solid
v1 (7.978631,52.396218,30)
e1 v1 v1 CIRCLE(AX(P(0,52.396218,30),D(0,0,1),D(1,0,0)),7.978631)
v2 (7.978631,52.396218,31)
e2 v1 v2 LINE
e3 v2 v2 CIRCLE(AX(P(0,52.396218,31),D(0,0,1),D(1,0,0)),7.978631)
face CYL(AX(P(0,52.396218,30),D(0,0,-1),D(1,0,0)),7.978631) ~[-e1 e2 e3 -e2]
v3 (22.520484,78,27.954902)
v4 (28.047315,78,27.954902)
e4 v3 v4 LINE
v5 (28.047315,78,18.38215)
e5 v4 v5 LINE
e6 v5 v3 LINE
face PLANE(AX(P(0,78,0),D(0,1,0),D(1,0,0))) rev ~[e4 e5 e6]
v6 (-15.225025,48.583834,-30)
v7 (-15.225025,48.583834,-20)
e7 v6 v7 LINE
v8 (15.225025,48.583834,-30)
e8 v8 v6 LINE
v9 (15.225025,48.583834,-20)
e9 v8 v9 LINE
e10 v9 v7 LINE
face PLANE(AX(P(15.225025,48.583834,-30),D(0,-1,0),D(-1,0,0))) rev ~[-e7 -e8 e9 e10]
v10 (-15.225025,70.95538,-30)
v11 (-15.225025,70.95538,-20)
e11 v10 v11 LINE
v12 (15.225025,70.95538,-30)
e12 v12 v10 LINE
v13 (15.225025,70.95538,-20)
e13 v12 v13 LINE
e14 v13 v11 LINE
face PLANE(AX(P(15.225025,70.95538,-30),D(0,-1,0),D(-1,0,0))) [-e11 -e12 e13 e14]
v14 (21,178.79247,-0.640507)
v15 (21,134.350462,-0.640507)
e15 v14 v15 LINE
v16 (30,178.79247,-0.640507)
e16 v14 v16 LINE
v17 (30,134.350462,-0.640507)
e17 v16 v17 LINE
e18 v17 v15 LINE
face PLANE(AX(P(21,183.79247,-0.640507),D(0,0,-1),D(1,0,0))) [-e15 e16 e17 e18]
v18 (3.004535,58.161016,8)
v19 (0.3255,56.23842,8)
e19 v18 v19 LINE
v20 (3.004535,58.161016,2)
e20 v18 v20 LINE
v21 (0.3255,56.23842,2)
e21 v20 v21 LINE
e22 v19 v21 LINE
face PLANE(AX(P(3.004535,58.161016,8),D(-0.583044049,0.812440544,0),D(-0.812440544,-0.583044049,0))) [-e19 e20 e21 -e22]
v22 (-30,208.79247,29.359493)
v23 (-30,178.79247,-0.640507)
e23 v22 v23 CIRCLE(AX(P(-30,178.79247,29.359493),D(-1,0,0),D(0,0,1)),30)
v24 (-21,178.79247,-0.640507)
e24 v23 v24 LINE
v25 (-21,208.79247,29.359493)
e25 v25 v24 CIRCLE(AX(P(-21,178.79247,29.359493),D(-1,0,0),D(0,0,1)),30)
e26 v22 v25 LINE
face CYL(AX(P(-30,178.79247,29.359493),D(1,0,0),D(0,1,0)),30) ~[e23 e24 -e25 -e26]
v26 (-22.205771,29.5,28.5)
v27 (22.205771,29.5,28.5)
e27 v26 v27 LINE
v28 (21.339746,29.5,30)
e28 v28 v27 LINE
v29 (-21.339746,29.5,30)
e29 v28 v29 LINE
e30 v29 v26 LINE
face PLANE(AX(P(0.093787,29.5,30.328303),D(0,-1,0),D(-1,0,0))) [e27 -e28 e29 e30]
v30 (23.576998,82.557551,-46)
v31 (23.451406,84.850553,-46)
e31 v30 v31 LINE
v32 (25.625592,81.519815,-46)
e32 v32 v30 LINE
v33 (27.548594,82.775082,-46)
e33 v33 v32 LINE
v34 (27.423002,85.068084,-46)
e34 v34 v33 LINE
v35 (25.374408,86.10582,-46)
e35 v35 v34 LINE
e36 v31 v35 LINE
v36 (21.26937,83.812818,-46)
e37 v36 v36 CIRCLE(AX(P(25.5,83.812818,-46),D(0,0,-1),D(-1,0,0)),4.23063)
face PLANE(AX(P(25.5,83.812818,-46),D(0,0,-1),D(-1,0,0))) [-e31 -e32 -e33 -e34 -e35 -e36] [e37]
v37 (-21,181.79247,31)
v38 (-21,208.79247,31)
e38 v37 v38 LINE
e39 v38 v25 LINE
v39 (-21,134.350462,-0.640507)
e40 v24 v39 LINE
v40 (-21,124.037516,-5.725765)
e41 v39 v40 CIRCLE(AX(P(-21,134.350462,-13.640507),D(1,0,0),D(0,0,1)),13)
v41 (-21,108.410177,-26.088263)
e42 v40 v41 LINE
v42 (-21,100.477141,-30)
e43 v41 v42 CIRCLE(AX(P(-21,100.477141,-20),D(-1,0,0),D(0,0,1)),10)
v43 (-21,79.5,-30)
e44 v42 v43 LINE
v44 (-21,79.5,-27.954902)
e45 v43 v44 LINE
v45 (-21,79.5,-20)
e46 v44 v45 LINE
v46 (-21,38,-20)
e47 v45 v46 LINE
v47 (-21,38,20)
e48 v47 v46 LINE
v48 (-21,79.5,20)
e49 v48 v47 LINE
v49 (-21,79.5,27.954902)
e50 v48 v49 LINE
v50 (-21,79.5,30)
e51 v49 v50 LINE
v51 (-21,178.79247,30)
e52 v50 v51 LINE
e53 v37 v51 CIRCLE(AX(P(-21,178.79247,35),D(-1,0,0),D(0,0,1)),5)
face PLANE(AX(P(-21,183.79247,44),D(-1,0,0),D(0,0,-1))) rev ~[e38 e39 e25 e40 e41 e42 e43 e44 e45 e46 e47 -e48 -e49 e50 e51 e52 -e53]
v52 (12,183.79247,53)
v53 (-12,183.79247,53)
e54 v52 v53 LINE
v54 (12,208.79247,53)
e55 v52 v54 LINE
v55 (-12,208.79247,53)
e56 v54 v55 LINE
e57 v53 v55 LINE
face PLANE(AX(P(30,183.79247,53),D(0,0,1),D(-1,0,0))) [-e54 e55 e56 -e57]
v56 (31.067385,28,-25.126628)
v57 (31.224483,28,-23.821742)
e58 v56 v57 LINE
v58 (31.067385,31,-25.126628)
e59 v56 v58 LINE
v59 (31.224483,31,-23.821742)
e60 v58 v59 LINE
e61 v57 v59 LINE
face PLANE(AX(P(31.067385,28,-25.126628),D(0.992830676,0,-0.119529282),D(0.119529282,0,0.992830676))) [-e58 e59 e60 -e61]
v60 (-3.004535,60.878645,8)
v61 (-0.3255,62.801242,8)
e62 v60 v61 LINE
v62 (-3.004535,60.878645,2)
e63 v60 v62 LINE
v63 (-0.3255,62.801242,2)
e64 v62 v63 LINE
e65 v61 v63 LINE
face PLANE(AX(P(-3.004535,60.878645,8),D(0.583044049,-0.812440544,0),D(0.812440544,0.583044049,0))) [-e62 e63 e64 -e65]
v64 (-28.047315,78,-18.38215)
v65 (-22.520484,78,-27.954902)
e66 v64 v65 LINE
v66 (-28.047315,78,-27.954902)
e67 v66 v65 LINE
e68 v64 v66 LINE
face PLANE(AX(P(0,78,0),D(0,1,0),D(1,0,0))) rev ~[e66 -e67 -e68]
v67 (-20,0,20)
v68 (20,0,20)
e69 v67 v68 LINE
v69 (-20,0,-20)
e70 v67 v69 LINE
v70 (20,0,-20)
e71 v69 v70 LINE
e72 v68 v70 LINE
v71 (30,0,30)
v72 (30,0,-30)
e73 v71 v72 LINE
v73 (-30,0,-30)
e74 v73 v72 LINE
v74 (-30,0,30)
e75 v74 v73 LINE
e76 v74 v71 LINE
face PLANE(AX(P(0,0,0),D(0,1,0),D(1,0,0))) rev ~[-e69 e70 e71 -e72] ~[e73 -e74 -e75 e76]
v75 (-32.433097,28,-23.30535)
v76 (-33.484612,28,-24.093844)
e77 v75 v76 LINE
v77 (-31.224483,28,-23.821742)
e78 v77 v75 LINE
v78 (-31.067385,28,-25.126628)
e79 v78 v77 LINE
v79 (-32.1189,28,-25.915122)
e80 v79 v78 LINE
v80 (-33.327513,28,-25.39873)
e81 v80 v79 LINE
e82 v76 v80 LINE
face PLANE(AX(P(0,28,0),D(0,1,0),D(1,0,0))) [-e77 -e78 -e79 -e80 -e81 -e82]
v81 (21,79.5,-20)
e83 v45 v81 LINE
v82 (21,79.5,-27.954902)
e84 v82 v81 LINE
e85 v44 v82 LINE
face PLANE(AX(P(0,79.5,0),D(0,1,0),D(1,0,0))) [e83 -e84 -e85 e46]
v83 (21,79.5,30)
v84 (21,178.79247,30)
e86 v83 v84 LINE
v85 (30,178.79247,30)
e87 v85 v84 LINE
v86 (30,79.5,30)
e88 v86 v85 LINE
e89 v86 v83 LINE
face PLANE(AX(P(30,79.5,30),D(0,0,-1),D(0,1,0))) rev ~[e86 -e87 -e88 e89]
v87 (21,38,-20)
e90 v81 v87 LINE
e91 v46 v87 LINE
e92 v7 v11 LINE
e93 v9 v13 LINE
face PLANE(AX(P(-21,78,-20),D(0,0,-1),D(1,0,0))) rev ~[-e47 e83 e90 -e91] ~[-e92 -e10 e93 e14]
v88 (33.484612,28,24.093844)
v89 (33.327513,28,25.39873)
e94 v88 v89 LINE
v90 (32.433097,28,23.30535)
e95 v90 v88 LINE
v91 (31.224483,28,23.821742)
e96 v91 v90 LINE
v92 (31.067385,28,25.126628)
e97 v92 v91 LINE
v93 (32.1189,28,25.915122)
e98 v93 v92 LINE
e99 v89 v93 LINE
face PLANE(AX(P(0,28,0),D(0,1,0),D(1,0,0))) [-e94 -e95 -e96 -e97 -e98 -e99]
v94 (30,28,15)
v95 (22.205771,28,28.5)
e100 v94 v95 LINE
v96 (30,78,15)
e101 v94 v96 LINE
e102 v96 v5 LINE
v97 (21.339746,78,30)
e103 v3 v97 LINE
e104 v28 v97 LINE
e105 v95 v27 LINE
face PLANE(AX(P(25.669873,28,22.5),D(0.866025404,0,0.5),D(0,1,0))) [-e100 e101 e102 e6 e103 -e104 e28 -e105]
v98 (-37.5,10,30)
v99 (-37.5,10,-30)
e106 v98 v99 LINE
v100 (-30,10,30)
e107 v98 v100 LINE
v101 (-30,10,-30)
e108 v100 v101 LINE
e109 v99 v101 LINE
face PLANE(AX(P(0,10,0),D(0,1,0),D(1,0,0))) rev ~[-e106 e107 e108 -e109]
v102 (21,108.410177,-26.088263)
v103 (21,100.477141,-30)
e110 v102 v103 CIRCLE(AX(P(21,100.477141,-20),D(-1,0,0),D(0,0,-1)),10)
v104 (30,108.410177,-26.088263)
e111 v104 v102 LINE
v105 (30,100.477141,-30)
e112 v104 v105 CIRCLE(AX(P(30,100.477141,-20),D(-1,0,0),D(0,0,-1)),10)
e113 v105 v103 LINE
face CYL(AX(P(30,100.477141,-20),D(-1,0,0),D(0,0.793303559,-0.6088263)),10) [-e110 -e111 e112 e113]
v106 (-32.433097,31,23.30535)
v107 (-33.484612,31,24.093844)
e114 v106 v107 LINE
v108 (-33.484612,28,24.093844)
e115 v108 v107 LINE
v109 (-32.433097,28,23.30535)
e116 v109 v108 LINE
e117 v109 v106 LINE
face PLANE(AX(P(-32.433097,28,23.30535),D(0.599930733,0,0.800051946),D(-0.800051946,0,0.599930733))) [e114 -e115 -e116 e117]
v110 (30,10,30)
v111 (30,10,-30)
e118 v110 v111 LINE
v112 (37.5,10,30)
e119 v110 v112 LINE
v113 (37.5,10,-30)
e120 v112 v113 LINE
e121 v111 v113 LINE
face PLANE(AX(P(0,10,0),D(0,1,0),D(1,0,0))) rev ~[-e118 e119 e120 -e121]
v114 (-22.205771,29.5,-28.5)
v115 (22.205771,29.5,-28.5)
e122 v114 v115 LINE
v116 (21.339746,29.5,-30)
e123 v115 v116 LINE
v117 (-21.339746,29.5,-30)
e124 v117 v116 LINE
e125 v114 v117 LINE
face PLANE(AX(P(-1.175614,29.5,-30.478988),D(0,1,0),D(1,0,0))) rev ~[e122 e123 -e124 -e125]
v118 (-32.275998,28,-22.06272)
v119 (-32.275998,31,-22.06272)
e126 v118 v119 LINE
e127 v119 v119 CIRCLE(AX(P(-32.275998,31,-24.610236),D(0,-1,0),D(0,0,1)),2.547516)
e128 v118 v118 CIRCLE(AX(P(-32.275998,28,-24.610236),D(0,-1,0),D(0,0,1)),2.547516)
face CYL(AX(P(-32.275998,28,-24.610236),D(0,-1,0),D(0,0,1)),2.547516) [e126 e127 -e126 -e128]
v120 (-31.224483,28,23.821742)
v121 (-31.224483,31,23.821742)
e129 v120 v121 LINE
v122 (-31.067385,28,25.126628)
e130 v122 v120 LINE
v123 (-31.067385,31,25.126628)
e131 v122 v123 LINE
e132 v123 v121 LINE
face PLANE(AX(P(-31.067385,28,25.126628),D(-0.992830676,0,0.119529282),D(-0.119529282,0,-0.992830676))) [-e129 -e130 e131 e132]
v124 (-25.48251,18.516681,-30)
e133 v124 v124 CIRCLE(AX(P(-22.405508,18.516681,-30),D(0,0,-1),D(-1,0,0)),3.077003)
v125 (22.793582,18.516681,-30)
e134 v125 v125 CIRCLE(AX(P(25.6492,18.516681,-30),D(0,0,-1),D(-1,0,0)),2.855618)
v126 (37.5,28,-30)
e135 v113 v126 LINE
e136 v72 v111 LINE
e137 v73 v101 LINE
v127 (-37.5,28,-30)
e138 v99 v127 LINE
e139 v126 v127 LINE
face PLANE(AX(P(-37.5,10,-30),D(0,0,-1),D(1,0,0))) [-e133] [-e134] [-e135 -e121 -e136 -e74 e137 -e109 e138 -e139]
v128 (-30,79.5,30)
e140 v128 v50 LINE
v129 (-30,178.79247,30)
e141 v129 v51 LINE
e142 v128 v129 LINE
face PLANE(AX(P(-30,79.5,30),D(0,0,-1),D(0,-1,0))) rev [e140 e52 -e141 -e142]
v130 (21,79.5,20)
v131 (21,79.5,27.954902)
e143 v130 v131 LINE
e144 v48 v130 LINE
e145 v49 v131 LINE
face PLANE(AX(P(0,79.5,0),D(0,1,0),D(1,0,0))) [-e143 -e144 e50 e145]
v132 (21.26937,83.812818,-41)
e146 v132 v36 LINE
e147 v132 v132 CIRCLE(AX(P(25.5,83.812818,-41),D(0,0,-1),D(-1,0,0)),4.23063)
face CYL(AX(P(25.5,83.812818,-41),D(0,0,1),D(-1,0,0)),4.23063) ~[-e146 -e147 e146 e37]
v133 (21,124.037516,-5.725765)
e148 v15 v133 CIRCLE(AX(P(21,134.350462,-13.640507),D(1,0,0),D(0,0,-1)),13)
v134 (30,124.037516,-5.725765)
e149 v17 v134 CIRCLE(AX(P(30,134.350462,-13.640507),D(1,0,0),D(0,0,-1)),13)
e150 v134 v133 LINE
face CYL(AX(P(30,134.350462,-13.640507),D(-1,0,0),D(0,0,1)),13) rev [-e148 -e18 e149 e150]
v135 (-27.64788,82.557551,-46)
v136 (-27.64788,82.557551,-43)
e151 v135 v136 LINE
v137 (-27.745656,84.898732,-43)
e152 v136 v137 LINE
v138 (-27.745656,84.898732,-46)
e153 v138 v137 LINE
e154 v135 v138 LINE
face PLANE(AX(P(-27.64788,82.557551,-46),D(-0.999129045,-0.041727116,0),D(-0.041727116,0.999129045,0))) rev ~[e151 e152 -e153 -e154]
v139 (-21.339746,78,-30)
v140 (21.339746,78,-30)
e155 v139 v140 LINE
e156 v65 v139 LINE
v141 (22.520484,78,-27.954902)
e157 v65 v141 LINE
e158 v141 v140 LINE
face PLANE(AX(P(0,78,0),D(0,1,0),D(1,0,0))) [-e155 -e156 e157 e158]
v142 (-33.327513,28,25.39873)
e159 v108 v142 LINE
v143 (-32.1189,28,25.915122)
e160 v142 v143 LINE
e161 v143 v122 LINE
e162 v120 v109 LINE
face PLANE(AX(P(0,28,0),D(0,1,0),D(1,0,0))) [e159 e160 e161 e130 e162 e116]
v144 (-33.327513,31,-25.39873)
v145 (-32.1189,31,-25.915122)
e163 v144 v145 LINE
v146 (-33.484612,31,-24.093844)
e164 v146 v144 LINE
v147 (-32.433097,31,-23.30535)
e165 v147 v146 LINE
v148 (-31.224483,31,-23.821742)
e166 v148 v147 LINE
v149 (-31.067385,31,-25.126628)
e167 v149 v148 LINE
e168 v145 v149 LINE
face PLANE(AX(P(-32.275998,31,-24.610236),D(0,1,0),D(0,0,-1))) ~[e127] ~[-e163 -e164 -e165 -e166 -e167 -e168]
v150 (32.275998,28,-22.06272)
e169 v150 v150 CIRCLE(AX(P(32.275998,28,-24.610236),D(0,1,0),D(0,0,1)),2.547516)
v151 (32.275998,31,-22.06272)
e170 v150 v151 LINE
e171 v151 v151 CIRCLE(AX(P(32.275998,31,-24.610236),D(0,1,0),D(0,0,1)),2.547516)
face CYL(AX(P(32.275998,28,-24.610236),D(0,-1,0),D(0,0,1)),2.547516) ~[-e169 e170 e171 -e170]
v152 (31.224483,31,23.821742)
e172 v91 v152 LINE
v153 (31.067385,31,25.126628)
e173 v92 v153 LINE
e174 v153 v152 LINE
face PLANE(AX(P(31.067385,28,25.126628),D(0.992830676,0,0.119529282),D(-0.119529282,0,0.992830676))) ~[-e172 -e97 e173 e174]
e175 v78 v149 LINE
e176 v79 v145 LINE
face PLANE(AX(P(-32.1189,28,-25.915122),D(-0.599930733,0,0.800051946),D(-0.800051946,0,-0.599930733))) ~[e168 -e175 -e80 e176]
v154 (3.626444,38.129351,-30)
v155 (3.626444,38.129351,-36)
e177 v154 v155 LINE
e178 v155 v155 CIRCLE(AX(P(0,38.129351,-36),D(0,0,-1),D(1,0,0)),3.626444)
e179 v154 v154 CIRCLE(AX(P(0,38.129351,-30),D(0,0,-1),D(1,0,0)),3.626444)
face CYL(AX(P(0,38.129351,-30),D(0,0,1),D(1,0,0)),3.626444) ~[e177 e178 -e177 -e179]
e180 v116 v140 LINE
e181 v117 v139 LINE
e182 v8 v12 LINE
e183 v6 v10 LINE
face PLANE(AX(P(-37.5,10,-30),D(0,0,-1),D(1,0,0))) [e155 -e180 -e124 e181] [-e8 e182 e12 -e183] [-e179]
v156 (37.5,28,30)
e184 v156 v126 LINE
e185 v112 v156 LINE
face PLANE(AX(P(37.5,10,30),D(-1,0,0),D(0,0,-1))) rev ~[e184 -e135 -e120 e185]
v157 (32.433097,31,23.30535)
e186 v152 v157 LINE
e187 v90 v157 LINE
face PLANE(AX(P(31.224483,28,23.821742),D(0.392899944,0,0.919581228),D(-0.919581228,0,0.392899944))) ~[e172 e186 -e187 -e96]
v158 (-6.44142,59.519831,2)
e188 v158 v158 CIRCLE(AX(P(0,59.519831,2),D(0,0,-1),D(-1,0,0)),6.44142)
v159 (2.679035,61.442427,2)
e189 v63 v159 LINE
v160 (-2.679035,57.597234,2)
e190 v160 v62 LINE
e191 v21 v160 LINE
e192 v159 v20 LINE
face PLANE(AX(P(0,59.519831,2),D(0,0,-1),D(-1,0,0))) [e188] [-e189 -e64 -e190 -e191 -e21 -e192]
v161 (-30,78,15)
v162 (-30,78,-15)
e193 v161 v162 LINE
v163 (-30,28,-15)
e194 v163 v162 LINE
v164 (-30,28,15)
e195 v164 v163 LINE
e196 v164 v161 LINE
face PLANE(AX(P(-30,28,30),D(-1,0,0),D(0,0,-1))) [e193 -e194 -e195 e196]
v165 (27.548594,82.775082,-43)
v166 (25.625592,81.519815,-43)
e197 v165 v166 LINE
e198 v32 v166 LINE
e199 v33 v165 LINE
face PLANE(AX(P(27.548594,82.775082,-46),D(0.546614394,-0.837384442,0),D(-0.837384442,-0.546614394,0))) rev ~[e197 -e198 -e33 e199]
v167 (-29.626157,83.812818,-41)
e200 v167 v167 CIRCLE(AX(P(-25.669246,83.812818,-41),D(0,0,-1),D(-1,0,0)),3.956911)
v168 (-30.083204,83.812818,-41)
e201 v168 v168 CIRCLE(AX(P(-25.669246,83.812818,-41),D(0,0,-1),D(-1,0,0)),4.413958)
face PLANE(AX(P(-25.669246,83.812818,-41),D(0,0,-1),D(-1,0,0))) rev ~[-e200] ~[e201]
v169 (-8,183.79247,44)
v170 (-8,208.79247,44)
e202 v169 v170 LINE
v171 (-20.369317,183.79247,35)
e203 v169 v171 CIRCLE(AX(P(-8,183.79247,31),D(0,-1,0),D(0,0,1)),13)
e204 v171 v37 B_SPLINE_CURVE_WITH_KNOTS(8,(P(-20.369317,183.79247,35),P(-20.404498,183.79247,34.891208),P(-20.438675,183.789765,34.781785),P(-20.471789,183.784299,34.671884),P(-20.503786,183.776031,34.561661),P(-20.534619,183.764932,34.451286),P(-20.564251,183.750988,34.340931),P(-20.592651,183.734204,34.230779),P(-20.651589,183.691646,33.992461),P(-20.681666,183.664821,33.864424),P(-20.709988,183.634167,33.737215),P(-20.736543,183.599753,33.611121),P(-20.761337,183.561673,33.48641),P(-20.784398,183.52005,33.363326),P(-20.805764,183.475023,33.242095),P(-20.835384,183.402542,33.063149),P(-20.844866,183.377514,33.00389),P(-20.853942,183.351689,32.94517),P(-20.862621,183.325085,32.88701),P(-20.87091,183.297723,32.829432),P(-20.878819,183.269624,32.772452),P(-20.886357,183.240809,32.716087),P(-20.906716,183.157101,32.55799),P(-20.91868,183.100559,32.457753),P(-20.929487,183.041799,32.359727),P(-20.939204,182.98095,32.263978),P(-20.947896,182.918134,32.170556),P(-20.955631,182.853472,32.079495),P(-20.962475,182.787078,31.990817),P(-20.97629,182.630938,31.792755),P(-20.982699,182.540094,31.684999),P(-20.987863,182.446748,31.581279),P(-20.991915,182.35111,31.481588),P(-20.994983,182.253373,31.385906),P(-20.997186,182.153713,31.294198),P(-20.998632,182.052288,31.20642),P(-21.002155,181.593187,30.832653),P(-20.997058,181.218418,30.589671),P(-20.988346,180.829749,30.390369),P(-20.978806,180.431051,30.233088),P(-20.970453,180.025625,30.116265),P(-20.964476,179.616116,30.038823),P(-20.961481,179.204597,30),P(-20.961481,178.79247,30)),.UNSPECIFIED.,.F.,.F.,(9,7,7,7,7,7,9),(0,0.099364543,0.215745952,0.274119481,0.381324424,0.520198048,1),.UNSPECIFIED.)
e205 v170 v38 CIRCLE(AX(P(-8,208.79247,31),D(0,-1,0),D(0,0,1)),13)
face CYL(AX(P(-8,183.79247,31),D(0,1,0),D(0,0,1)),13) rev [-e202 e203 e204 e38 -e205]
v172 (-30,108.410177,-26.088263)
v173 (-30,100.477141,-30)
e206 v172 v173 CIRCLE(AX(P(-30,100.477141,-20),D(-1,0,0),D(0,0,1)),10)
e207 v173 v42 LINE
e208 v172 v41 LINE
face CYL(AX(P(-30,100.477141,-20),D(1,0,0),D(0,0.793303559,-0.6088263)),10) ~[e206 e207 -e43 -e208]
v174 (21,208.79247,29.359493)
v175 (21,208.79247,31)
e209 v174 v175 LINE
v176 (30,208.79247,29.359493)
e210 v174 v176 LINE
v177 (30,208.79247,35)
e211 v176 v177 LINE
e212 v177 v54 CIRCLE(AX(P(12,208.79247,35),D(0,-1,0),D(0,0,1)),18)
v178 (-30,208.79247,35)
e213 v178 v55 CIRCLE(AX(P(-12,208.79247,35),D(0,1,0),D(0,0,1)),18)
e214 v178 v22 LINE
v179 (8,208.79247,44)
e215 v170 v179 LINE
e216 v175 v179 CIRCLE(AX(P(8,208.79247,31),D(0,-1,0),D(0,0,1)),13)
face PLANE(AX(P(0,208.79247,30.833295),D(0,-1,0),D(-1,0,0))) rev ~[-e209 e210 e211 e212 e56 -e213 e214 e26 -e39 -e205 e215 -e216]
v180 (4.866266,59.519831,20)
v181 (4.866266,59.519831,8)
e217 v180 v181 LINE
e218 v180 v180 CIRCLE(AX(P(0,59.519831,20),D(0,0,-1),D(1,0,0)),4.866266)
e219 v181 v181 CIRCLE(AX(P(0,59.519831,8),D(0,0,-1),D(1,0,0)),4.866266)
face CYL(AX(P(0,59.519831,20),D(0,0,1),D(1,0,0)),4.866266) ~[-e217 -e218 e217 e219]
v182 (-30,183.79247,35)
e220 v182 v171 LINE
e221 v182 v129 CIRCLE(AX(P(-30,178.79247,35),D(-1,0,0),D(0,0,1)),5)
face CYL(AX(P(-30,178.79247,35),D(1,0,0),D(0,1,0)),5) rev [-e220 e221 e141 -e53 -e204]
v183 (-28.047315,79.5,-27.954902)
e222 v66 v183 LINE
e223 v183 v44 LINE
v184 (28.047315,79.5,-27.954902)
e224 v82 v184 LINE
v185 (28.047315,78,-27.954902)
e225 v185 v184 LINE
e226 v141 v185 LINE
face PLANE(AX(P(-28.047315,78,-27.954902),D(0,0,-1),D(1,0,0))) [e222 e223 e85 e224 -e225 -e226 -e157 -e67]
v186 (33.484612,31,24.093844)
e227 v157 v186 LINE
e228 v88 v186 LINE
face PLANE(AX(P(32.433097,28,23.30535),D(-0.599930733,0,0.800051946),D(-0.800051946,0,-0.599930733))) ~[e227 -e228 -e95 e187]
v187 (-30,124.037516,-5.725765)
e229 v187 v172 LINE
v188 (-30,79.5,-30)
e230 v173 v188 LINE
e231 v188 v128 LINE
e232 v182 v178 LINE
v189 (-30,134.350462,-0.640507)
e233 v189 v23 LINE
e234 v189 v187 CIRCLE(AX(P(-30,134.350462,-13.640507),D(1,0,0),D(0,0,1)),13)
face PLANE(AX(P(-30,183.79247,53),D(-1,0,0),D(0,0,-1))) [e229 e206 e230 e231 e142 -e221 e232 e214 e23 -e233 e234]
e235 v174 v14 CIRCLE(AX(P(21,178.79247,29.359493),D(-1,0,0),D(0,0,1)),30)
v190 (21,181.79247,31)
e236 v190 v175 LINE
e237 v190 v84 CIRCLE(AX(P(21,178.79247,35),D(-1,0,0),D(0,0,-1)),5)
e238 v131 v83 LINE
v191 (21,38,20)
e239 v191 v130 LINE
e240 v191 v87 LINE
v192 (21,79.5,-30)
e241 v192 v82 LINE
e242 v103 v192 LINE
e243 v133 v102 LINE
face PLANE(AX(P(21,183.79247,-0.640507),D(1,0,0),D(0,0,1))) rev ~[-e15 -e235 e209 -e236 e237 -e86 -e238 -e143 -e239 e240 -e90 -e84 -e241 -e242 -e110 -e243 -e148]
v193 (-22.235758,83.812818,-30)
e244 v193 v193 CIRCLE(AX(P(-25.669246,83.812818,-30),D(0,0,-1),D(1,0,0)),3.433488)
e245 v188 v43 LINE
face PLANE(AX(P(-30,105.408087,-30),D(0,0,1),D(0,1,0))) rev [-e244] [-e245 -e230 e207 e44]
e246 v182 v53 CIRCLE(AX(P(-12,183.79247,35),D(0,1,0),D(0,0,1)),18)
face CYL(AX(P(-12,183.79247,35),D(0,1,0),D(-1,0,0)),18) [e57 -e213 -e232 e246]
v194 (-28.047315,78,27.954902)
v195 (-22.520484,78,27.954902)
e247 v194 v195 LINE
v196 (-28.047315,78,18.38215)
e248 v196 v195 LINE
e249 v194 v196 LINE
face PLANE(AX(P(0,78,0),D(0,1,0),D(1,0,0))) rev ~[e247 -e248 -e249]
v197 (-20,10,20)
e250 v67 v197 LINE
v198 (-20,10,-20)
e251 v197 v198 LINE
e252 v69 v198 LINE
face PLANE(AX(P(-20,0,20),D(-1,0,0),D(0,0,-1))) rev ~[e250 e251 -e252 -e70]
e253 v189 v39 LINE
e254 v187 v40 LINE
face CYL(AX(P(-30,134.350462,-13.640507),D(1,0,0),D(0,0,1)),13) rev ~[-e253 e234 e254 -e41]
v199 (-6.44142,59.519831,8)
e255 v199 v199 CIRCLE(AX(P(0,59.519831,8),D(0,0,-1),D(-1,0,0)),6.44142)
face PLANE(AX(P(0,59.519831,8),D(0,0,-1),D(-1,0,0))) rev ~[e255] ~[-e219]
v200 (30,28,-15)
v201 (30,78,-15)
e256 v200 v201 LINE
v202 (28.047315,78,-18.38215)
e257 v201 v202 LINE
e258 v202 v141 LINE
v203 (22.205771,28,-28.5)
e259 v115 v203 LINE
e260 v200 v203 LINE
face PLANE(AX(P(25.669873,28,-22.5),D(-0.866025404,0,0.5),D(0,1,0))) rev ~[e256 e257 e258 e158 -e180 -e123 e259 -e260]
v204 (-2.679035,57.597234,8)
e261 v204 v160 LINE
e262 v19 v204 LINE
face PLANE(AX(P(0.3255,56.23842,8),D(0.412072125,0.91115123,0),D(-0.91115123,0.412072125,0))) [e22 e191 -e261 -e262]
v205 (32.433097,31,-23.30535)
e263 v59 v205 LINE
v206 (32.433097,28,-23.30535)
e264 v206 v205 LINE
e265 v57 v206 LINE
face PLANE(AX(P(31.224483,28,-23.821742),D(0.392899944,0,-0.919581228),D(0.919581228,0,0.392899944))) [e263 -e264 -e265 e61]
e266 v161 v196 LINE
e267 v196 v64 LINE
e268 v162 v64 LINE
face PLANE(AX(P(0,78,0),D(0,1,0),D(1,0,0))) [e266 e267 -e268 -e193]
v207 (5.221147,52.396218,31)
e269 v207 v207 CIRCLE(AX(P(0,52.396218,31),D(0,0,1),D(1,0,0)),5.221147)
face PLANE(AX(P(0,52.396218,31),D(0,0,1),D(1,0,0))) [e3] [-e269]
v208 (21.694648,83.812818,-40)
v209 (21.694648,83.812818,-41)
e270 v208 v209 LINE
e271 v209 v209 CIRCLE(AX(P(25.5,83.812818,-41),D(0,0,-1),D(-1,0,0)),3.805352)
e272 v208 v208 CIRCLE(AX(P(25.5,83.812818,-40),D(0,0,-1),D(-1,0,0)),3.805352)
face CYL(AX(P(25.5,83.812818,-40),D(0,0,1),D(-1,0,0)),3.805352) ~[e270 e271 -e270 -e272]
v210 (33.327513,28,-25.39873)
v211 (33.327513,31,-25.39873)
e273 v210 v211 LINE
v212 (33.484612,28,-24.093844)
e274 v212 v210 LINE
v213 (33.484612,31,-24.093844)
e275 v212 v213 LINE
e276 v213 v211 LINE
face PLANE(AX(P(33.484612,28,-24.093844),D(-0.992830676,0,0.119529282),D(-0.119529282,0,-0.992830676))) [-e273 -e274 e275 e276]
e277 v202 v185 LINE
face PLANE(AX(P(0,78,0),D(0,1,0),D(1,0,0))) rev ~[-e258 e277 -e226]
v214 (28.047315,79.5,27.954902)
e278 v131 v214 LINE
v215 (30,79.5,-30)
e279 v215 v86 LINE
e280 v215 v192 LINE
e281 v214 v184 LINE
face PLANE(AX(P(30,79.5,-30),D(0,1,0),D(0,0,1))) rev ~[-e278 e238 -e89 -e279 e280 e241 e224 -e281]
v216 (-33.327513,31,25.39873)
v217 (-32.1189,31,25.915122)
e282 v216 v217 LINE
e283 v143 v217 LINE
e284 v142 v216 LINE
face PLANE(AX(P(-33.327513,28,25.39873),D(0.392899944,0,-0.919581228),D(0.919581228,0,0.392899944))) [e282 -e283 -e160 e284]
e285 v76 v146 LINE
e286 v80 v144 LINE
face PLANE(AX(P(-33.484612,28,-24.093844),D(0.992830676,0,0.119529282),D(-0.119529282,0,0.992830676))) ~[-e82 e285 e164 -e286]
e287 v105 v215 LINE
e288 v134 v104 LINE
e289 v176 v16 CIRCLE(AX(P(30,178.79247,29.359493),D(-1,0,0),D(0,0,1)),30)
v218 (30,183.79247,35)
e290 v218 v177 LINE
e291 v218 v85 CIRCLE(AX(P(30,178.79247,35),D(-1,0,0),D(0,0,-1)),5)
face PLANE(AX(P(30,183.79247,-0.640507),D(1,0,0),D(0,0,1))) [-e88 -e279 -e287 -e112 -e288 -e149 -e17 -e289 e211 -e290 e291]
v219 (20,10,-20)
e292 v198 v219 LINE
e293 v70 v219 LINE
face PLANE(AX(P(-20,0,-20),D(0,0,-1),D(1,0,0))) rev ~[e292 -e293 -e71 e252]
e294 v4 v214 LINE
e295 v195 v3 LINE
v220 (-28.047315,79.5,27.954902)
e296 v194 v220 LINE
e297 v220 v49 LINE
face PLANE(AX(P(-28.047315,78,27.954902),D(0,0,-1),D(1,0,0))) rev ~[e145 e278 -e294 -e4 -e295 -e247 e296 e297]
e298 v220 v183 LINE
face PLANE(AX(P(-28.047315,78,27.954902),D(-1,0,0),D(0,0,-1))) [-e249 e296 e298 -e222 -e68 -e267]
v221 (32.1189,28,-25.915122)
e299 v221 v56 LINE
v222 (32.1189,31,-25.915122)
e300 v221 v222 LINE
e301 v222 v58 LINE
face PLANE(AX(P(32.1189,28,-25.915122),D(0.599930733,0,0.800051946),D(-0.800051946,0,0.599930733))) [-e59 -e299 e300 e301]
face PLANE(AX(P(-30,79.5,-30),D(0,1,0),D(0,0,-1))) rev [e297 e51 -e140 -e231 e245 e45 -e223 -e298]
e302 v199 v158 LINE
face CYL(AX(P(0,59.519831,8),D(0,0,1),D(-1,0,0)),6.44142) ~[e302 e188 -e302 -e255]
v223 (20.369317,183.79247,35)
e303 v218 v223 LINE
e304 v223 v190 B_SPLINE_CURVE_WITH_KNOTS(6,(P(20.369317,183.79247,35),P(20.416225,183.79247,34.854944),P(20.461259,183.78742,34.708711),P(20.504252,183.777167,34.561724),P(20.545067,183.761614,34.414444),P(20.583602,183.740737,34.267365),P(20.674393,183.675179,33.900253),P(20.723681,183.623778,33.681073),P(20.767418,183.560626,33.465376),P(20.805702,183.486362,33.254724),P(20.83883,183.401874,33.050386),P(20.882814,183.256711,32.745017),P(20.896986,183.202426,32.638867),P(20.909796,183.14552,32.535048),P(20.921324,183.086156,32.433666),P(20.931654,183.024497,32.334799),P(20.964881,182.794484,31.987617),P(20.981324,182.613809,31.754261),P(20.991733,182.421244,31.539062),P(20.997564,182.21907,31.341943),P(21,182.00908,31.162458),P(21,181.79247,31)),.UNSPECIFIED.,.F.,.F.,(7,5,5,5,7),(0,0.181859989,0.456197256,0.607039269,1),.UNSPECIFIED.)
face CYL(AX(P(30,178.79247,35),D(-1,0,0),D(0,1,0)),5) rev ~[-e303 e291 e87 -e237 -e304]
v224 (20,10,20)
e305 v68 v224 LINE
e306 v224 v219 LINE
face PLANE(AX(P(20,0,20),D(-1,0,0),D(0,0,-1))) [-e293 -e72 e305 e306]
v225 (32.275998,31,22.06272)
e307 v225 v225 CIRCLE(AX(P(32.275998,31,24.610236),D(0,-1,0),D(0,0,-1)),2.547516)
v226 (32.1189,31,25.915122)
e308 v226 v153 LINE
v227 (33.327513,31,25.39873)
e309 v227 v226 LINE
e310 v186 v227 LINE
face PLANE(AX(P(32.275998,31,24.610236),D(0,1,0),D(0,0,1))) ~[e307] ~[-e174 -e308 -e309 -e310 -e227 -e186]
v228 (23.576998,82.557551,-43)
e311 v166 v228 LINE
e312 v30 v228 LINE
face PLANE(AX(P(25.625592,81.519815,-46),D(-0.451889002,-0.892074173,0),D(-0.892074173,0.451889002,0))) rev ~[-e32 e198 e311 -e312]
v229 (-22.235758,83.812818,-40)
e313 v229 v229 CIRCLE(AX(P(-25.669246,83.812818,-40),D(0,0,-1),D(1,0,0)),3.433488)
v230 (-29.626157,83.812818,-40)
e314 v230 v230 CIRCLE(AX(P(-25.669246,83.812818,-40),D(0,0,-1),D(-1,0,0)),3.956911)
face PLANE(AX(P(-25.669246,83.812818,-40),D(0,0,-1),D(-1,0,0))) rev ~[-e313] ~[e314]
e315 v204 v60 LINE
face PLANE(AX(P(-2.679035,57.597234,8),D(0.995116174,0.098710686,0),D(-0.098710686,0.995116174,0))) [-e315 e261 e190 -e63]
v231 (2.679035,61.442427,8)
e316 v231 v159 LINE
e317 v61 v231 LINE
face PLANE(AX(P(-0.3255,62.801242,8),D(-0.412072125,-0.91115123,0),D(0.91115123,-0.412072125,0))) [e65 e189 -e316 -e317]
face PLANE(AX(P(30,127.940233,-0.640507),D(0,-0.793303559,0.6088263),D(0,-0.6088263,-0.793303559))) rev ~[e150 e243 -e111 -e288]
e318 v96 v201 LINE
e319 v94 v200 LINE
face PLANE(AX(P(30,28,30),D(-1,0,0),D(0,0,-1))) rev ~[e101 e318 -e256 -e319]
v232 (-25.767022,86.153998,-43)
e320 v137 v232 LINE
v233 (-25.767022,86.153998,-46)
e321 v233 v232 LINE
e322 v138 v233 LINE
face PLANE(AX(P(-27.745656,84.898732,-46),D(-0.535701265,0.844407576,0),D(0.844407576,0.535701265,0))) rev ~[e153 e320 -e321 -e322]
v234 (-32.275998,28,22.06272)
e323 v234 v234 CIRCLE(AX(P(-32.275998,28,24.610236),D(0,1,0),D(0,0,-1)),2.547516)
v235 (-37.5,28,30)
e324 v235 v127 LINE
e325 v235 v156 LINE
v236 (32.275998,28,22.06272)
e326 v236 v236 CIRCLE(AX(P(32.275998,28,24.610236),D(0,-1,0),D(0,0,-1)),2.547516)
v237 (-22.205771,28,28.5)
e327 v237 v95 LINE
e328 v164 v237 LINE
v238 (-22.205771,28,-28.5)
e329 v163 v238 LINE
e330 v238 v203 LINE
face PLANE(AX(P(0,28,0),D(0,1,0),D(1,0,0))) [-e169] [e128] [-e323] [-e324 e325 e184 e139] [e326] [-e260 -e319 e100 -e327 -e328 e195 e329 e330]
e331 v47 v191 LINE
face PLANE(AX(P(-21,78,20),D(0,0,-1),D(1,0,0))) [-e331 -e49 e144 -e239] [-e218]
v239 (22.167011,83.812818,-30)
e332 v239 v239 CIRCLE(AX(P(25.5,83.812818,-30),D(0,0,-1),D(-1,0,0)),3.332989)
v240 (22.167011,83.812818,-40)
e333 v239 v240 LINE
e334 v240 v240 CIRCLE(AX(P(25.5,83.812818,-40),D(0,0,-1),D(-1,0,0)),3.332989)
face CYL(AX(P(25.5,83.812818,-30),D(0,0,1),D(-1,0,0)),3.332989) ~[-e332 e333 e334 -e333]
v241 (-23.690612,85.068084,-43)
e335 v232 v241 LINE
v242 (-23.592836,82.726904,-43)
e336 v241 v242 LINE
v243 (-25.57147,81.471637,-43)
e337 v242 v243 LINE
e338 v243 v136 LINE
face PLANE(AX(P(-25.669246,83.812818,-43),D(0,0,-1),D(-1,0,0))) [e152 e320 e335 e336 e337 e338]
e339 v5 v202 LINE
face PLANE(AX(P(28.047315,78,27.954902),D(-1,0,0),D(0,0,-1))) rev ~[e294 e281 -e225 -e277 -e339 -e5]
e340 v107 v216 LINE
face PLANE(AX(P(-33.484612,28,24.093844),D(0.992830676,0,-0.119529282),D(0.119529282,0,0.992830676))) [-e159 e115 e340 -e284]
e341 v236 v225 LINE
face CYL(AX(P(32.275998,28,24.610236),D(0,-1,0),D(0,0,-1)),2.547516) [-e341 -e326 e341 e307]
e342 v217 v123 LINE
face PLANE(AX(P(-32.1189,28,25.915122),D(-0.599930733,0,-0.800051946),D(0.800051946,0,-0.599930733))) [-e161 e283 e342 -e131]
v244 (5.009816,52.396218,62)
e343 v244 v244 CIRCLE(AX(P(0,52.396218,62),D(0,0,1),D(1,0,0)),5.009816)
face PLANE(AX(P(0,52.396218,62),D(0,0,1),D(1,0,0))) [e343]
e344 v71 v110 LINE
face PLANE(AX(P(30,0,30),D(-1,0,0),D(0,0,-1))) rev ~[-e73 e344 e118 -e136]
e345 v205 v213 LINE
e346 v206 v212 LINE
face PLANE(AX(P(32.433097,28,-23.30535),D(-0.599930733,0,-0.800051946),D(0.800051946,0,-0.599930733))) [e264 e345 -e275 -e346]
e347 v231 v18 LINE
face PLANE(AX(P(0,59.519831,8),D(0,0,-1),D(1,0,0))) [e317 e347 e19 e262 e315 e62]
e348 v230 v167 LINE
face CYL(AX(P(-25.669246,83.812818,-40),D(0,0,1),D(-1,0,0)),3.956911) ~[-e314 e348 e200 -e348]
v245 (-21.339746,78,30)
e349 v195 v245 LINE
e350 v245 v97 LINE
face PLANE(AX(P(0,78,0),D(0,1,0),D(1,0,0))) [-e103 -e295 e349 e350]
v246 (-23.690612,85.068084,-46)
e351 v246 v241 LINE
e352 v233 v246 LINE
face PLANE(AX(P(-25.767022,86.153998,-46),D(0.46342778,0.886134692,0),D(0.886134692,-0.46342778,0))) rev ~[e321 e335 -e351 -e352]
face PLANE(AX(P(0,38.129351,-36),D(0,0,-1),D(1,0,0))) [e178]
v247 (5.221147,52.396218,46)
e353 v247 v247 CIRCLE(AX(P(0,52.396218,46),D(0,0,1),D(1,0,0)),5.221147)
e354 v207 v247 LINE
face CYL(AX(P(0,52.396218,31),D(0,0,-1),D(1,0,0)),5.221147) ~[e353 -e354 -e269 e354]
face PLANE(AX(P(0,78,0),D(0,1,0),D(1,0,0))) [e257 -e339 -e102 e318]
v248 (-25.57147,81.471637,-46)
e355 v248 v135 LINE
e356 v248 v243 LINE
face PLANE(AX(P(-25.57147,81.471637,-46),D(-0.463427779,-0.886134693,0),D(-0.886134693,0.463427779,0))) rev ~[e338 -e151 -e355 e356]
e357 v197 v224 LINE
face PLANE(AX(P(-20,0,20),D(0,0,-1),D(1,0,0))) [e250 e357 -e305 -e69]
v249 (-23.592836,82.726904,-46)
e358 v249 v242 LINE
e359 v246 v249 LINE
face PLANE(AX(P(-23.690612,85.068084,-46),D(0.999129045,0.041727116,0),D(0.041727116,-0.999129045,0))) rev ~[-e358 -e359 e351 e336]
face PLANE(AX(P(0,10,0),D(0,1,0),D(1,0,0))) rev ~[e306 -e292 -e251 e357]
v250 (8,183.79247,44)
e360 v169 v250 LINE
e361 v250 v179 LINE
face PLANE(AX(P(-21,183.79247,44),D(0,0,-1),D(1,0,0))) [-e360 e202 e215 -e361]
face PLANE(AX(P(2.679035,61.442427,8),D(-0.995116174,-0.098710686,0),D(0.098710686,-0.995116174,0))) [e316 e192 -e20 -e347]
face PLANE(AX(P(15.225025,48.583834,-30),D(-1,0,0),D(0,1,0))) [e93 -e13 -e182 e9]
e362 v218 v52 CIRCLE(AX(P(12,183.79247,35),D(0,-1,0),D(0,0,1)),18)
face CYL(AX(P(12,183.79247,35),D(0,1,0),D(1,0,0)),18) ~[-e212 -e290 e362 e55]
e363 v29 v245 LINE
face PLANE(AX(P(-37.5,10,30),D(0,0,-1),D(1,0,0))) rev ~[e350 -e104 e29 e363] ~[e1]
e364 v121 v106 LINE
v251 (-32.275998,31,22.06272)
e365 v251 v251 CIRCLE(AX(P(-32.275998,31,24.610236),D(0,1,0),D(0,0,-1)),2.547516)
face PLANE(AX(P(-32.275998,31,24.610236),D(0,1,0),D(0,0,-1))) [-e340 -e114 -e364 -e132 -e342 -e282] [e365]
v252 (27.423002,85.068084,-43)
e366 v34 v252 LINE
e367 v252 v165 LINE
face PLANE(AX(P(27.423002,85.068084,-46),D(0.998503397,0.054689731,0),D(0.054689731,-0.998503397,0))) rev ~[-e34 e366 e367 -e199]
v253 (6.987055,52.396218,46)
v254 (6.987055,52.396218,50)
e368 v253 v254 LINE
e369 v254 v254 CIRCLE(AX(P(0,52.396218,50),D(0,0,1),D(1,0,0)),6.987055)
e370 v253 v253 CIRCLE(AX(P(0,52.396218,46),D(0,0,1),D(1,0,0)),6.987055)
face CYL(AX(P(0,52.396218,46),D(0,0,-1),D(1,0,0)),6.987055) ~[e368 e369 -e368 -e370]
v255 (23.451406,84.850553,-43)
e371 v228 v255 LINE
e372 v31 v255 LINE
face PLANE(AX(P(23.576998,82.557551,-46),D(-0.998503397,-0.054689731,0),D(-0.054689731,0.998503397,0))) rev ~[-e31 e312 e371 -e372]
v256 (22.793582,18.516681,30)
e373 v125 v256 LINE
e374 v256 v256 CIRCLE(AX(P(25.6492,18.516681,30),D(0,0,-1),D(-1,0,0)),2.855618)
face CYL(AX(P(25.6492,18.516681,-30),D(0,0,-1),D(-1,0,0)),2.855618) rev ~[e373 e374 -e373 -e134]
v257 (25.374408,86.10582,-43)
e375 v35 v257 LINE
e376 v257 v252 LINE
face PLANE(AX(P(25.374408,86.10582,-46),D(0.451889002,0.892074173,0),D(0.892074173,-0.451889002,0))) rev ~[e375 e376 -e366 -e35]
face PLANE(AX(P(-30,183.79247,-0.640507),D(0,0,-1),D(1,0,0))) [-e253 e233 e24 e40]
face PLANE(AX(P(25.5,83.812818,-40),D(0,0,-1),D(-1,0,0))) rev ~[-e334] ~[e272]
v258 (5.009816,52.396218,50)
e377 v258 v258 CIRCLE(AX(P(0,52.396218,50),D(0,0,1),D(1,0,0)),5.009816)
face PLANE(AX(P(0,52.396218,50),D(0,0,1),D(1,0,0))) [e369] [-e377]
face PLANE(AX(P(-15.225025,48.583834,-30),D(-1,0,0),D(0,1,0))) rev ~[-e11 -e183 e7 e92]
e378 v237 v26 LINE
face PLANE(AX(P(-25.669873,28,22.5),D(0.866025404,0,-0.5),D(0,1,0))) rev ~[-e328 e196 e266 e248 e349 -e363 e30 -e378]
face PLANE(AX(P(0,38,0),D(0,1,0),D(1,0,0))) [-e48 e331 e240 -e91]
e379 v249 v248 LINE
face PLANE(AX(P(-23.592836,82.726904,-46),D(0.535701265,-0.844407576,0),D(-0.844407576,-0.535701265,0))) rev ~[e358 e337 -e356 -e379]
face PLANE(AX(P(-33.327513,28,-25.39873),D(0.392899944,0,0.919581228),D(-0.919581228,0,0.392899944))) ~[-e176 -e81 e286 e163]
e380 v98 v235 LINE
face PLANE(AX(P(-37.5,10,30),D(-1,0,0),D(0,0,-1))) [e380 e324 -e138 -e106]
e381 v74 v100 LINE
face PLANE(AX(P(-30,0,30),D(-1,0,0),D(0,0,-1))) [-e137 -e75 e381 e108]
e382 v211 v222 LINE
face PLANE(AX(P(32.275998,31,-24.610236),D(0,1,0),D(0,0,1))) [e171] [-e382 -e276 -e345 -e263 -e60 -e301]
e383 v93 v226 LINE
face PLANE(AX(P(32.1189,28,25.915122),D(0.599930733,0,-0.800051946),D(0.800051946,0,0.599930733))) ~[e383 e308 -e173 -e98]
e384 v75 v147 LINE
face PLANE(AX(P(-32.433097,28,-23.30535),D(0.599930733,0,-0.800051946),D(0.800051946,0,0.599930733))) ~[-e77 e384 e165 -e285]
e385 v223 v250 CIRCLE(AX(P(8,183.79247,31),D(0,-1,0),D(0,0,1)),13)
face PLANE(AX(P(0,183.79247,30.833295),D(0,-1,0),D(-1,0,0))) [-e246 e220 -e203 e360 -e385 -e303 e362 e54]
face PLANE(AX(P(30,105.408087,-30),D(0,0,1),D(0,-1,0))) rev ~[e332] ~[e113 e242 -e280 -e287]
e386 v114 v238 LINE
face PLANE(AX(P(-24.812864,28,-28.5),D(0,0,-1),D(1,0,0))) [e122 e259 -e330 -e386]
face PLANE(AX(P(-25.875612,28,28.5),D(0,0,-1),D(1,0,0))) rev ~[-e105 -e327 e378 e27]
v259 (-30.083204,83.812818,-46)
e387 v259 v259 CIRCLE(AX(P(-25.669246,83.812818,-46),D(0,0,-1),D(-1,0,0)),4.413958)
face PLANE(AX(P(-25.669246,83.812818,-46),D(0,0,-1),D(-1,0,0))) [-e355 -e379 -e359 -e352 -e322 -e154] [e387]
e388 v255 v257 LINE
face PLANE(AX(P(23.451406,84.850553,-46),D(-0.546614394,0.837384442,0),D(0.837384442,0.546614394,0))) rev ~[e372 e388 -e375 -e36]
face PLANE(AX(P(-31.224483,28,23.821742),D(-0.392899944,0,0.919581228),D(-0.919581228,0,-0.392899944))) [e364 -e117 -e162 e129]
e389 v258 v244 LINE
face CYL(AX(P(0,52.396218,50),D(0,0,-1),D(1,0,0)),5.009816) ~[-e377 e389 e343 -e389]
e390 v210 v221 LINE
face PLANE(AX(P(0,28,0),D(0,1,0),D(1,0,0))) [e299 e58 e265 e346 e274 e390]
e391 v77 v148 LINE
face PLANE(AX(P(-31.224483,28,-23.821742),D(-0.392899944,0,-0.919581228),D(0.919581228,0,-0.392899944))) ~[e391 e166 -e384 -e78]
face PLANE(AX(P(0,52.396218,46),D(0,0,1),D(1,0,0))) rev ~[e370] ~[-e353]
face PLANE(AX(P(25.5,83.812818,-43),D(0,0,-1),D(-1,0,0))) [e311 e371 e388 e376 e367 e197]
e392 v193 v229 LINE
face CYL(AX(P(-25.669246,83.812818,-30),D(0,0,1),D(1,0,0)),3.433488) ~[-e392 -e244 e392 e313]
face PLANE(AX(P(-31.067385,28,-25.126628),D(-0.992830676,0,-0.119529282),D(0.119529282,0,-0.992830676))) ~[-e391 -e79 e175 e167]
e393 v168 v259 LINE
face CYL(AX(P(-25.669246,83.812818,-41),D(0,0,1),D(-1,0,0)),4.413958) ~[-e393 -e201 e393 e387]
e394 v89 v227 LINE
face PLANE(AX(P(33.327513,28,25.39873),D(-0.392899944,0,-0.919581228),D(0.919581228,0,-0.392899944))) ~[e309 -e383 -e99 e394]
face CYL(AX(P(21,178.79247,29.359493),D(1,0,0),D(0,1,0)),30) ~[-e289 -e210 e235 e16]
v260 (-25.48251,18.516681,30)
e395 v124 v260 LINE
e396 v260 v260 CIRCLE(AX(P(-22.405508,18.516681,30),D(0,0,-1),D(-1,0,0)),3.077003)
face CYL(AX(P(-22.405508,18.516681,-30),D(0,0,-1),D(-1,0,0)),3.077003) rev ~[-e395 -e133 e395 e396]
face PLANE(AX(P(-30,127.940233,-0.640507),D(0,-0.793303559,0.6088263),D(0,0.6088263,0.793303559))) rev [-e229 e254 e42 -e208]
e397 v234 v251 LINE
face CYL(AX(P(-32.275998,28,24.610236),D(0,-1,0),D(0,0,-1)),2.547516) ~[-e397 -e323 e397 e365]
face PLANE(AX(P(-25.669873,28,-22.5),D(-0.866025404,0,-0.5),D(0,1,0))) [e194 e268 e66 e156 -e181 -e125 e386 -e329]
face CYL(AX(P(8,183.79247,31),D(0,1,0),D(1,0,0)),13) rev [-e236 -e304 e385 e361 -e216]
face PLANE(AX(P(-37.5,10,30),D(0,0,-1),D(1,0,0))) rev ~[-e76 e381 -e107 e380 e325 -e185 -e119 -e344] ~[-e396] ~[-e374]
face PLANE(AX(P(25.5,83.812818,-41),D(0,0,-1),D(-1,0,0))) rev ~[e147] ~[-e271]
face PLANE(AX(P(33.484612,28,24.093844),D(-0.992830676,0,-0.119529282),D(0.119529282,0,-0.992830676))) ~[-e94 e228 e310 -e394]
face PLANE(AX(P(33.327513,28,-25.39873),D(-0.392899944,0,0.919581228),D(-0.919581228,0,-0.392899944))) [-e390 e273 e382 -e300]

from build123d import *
from OCP.BRepFilletAPI import BRepFilletAPI_MakeChamfer

# Parameters (mm, degrees)
SKETCH1_W               = 60
SKETCH1_H               = 60
SKETCH1_W_2             = 40
SKETCH1_H_2             = 40
BOSS_EXTRUDE1_DEPTH     = 10
SKETCH2_W               = 75
SKETCH2_H               = 60
BOSS_EXTRUDE2_DEPTH     = 18
SKETCH4_W               = 60
SKETCH4_H               = 60
BOSS_EXTRUDE3_DEPTH     = 50
CHAMFER1_SIZE           = 15
CHAMFER1_SIZE2          = 8.660254038
CHAMFER2_SIZE           = 15
CHAMFER2_SIZE2          = 8.660254038
SKETCH5_W               = 30.45005041
SKETCH5_H               = 22.37154602
CUT_EXTRUDE1_DEPTH      = 20
CUT_EXTRUDE2_DEPTH      = 1.5
SKETCH7_R               = 2.547515883
BOSS_EXTRUDE4_DEPTH     = 3
MIRROR4_COPY_1_SKETCH_R = 2.547515883
MIRROR4_COPY_1_DEPTH    = 3
CUT_EXTRUDE3_REACH      = 107.31
SKETCH8_R               = 2.85561841
SKETCH8_R_2             = 3.077002641
SKETCH10_W              = 42
SKETCH10_H              = 40
CUT_EXTRUDE4_DEPTH      = 40
BOSS_EXTRUDE5_DEPTH     = 9
SKETCH12_W              = 56.09463004
SKETCH12_H              = 55.909804242
SKETCH12_W_2            = 42
SKETCH12_H_2            = 40
BOSS_EXTRUDE6_DEPTH     = 1.5
BOSS_EXTRUDE7_DEPTH     = 25
FILLET1_R               = 18
FILLET2_R               = 13
FILLET3_R               = 13
FILLET4_R               = 10
FILLET6_R               = 5
FILLET7_R               = 30
SKETCH14_R              = 3.332988603
SKETCH14_R_2            = 3.433487648
BOSS_EXTRUDE8_DEPTH     = 10
SKETCH15_R              = 3.805352351
SKETCH15_R_2            = 3.956911339
BOSS_EXTRUDE9_DEPTH     = 1
SKETCH16_R              = 4.230629521
SKETCH16_R_2            = 4.413958077
BOSS_EXTRUDE10_DEPTH    = 5
CUT_EXTRUDE5_DEPTH      = 3
SKETCH18_R              = 7.978631378
BOSS_EXTRUDE11_DEPTH    = 1
SKETCH19_R              = 5.221147189
BOSS_EXTRUDE12_DEPTH    = 15
SKETCH20_R              = 6.98705533
BOSS_EXTRUDE13_DEPTH    = 4
SKETCH21_R              = 5.009815996
BOSS_EXTRUDE14_DEPTH    = 12
SKETCH22_R              = 4.866265591
BOSS_EXTRUDE15_DEPTH    = 12
SKETCH23_R              = 6.441420435
BOSS_EXTRUDE16_DEPTH    = 6
SKETCH24_R              = 3.62644416
BOSS_EXTRUDE17_DEPTH    = 6


with BuildPart() as part:
    # Sketch1 → Boss-Extrude1 (new body)
    with BuildSketch(Plane(origin=(0, 0, 0), x_dir=(1, 0, 0), z_dir=(0, 1, 0))):
        Rectangle(SKETCH1_W, SKETCH1_H)
        Rectangle(SKETCH1_W_2, SKETCH1_H_2, mode=Mode.SUBTRACT)
    extrude(amount=BOSS_EXTRUDE1_DEPTH)

    # Sketch2 → Boss-Extrude2 (add)
    with BuildSketch(Plane(origin=(0, 10, 0), x_dir=(1, 0, 0), z_dir=(0, 1, 0))):
        Rectangle(SKETCH2_W, SKETCH2_H)
    extrude(amount=BOSS_EXTRUDE2_DEPTH)

    # Sketch4 → Boss-Extrude3 (add)
    with BuildSketch(Plane(origin=(0, 28, 0), x_dir=(1, 0, 0), z_dir=(0, 1, 0))):
        Rectangle(SKETCH4_W, SKETCH4_H)
    extrude(amount=BOSS_EXTRUDE3_DEPTH)

    # Chamfer1: one chamfer whose edges measure the first distance from different faces: ONE call of the kernel's chamfer builder (chamfer() names one face for all edges)
    chamfer1_edges_1 = [part.edges().sort_by_distance(p)[0] for p in [
        (-30, 53, 30),
    ]]
    chamfer1_side_1 = [part.faces().sort_by_distance(p)[0] for p in [
        (-30, 53, 0),
    ]]
    chamfer1_edges_2 = [part.edges().sort_by_distance(p)[0] for p in [
        (30, 53, -30),
    ]]
    chamfer1_side_2 = [part.faces().sort_by_distance(p)[0] for p in [
        (30, 53, 0),
    ]]
    chamfer1 = BRepFilletAPI_MakeChamfer(part.part.solid().wrapped)
    for e in chamfer1_edges_1:
        chamfer1.Add(CHAMFER1_SIZE, CHAMFER1_SIZE2, e.wrapped, chamfer1_side_1[0].wrapped)  # the first distance lies on this face
    for e in chamfer1_edges_2:
        chamfer1.Add(CHAMFER1_SIZE, CHAMFER1_SIZE2, e.wrapped, chamfer1_side_2[0].wrapped)  # the first distance lies on this face
    add(Compound.cast(chamfer1.Shape()), mode=Mode.REPLACE)

    # Chamfer2: one chamfer whose edges measure the first distance from different faces: ONE call of the kernel's chamfer builder (chamfer() names one face for all edges)
    chamfer2_edges_1 = [part.edges().sort_by_distance(p)[0] for p in [
        (-30, 53, -30),
    ]]
    chamfer2_side_1 = [part.faces().sort_by_distance(p)[0] for p in [
        (-30, 53, -7.5),
    ]]
    chamfer2_edges_2 = [part.edges().sort_by_distance(p)[0] for p in [
        (30, 53, 30),
    ]]
    chamfer2_side_2 = [part.faces().sort_by_distance(p)[0] for p in [
        (30, 53, 7.5),
    ]]
    chamfer2 = BRepFilletAPI_MakeChamfer(part.part.solid().wrapped)
    for e in chamfer2_edges_1:
        chamfer2.Add(CHAMFER2_SIZE, CHAMFER2_SIZE2, e.wrapped, chamfer2_side_1[0].wrapped)  # the first distance lies on this face
    for e in chamfer2_edges_2:
        chamfer2.Add(CHAMFER2_SIZE, CHAMFER2_SIZE2, e.wrapped, chamfer2_side_2[0].wrapped)  # the first distance lies on this face
    add(Compound.cast(chamfer2.Shape()), mode=Mode.REPLACE)

    # Sketch5 → Cut-Extrude1 (cut)
    with BuildSketch(Plane(origin=(0, 0, -30), x_dir=(-1, 0, 0), z_dir=(0, 0, -1))):
        with Locations((0, 59.769606645)):
            Rectangle(SKETCH5_W, SKETCH5_H)
    extrude(amount=-CUT_EXTRUDE1_DEPTH, mode=Mode.SUBTRACT)

    # Sketch6 → Cut-Extrude2 (cut)
    with BuildSketch(Plane(origin=(0, 28, 0), x_dir=(1, 0, 0), z_dir=(0, 1, 0))):
        Polygon((-24.812863535, 28.5), (23.79632164, 28.5), (23.79632164, 32.381341782), (-26.938360226, 32.381341782), align=None)
        Polygon((-25.87561188, -28.5), (26.568708627, -28.5), (25.367340933, -32.196515983), (-25.87561188, -32.196515983), align=None)
    extrude(amount=CUT_EXTRUDE2_DEPTH, mode=Mode.SUBTRACT)

    # Sketch7 → Boss-Extrude4 (add)
    with BuildSketch(Plane(origin=(0, 28, 0), x_dir=(1, 0, 0), z_dir=(0, 1, 0))):
        with Locations(Location((32.275998147, 24.610235837, 0), (0, 0, 270))):
            Circle(SKETCH7_R)
        Polygon((33.484611692, 24.093844051), (33.327513325, 25.398729977), (32.118899781, 25.915121764), (31.067384603, 25.126627624), (31.22448297, 23.821741698), (32.433096514, 23.305349911), align=None, mode=Mode.SUBTRACT)
    boss_extrude4 = extrude(amount=BOSS_EXTRUDE4_DEPTH)

    # Mirror3: Boss-Extrude4 across plane
    add(boss_extrude4.mirror(Plane(origin=(0, 0, 0), x_dir=(0, 0, 1), z_dir=(1, 0, 0))))

    # Mirror4: Boss-Extrude4 across plane
    add(boss_extrude4.mirror(Plane.XY))

    # Mirror4 copy 1 sketch → Mirror4 copy 1 (add)
    with BuildSketch(Plane(origin=(0, 28, 0), x_dir=(-1, 0, 0), z_dir=(0, 1, 0))):
        with Locations(Location((32.275998147, 24.610235837, 0), (0, 0, 270))):
            Circle(MIRROR4_COPY_1_SKETCH_R)
        Polygon((33.484611692, 24.093844051), (33.327513325, 25.398729977), (32.118899781, 25.915121764), (31.067384603, 25.126627624), (31.22448297, 23.821741698), (32.433096514, 23.305349911), align=None, mode=Mode.SUBTRACT)
    extrude(amount=MIRROR4_COPY_1_DEPTH)

    # Sketch8 → Cut-Extrude3 (cut, up to next)
    with BuildSketch(Plane(origin=(0, 0, -30), x_dir=(-1, 0, 0), z_dir=(0, 0, -1)), mode=Mode.PRIVATE) as cut_extrude3_sk1:
        with Locations((-25.649200277, 18.51668081)):
            Circle(SKETCH8_R)
    cut_extrude3_tool1 = extrude(cut_extrude3_sk1.sketch, amount=-CUT_EXTRUDE3_REACH, mode=Mode.PRIVATE) & part.part
    # Sketch8 → Cut-Extrude3 (cut, up to next)
    with BuildSketch(Plane(origin=(0, 0, -30), x_dir=(-1, 0, 0), z_dir=(0, 0, -1)), mode=Mode.PRIVATE) as cut_extrude3_sk2:
        with Locations((22.405507501, 18.51668081)):
            Circle(SKETCH8_R_2)
    cut_extrude3_tool2 = extrude(cut_extrude3_sk2.sketch, amount=-CUT_EXTRUDE3_REACH, mode=Mode.PRIVATE) & part.part
    add(cut_extrude3_tool1.solids().sort_by_distance((25.6492, 18.516681, -30))[0], mode=Mode.SUBTRACT)
    add(cut_extrude3_tool2.solids().sort_by_distance((-22.405508, 18.516681, -30))[0], mode=Mode.SUBTRACT)

    # Sketch10 → Cut-Extrude4 (cut)
    with BuildSketch(Plane(origin=(0, 78, 0), x_dir=(1, 0, 0), z_dir=(0, 1, 0))):
        Rectangle(SKETCH10_W, SKETCH10_H)
    extrude(amount=-CUT_EXTRUDE4_DEPTH, mode=Mode.SUBTRACT)



with BuildPart() as body_2:
    # Sketch11 → Boss-Extrude5 (new body)
    with BuildSketch(Plane(origin=(30, 0, 0), x_dir=(0, 0, -1), z_dir=(1, 0, 0))):
        Polygon((-30, 79.5), (-30, 183.792470171), (0.640507311, 183.792470171), (0.640507311, 127.940232676), (30, 105.408087073), (30, 79.5), align=None)
    boss_extrude5 = extrude(amount=-BOSS_EXTRUDE5_DEPTH)


with BuildPart() as part_1:
    add(part.part)

    add(body_2.part)  # Boss-Extrude6 merges body 2
    # Sketch12 → Boss-Extrude6 (add)
    with BuildSketch(Plane(origin=(0, 78, 0), x_dir=(1, 0, 0), z_dir=(0, 1, 0))):
        Rectangle(SKETCH12_W, SKETCH12_H)
        Rectangle(SKETCH12_W_2, SKETCH12_H_2, mode=Mode.SUBTRACT)
    extrude(amount=BOSS_EXTRUDE6_DEPTH)

    # Mirror5: Boss-Extrude5 across plane
    add(boss_extrude5.mirror(Plane(origin=(0, 0, 0), x_dir=(0, 0, 1), z_dir=(1, 0, 0))))

    # Sketch13 → Boss-Extrude7 (add)
    with BuildSketch(Plane(origin=(0, 183.792470171, 0), x_dir=(1, 0, 0), z_dir=(0, 1, 0))):
        Polygon((-30, 0.640507311), (-21, 0.640507311), (-21, -30), (-21, -44), (21, -44), (21, -30), (21, 0.640507311), (30, 0.640507311), (30, -53), (-30, -53), align=None)
    extrude(amount=BOSS_EXTRUDE7_DEPTH)

    # Fillet1
    fillet1_edges = [part_1.edges().sort_by_distance(p)[0] for p in [
        (-30, 196.292470171, 53),
        (30, 196.292470171, 53),
    ]]
    fillet(fillet1_edges, radius=FILLET1_R)

    # Fillet2
    fillet2_edges = [part_1.edges().sort_by_distance(p)[0] for p in [
        (21, 196.292470171, 44),
        (-21, 196.292470171, 44),
    ]]
    fillet(fillet2_edges, radius=FILLET2_R)

    # Fillet3
    fillet3_edges = [part_1.edges().sort_by_distance(p)[0] for p in [
        (25.5, 127.940232676, -0.640507311),
        (-25.5, 127.940232676, -0.640507311),
    ]]
    fillet(fillet3_edges, radius=FILLET3_R)

    # Fillet4
    fillet4_edges = [part_1.edges().sort_by_distance(p)[0] for p in [
        (25.5, 105.408087073, -30),
        (-25.5, 105.408087073, -30),
    ]]
    fillet(fillet4_edges, radius=FILLET4_R)

    # Fillet6
    fillet6_edges = [part_1.edges().sort_by_distance(p)[0] for p in [
        (-25.5, 183.792470171, 30),
        (25.5, 183.792470171, 30),
    ]]
    fillet(fillet6_edges, radius=FILLET6_R)

    # Fillet7
    fillet7_edges = [part_1.edges().sort_by_distance(p)[0] for p in [
        (25.5, 208.792470171, -0.640507311),
        (-25.5, 208.792470171, -0.640507311),
    ]]
    fillet(fillet7_edges, radius=FILLET7_R)

    # Sketch14 → Boss-Extrude8 (add)
    with BuildSketch(Plane(origin=(0, 0, -30), x_dir=(-1, 0, 0), z_dir=(0, 0, -1))):
        with Locations((-25.5, 83.812817652)):
            Circle(SKETCH14_R)
        with Locations(Location((25.669245773, 83.812817652, 0), (0, 0, 180))):
            Circle(SKETCH14_R_2)
    extrude(amount=BOSS_EXTRUDE8_DEPTH)

    # Sketch15 → Boss-Extrude9 (add)
    with BuildSketch(Plane(origin=(0, 0, -40), x_dir=(-1, 0, 0), z_dir=(0, 0, -1))):
        with Locations((-25.5, 83.812817652)):
            Circle(SKETCH15_R)
        with Locations((25.669245773, 83.812817652)):
            Circle(SKETCH15_R_2)
    extrude(amount=BOSS_EXTRUDE9_DEPTH)

    # Sketch16 → Boss-Extrude10 (add)
    with BuildSketch(Plane(origin=(0, 0, -41), x_dir=(-1, 0, 0), z_dir=(0, 0, -1))):
        with Locations((-25.5, 83.812817652)):
            Circle(SKETCH16_R)
        with Locations((25.669245773, 83.812817652)):
            Circle(SKETCH16_R_2)
    extrude(amount=BOSS_EXTRUDE10_DEPTH)

    # Sketch17 → Cut-Extrude5 (cut)
    with BuildSketch(Plane(origin=(0, 0, -46), x_dir=(-1, 0, 0), z_dir=(0, 0, -1))):
        Polygon((-23.5769975, 82.557550901), (-23.451405856, 84.850553293), (-25.374408356, 86.105820043), (-27.4230025, 85.068084402), (-27.548594144, 82.77508201), (-25.625591644, 81.51981526), align=None)
        Polygon((27.647879806, 82.557550901), (27.745655684, 84.898731614), (25.767021651, 86.153998364), (23.690611741, 85.068084402), (23.592835863, 82.72690369), (25.571469895, 81.47163694), align=None)
    extrude(amount=-CUT_EXTRUDE5_DEPTH, mode=Mode.SUBTRACT)

    # Sketch18 → Boss-Extrude11 (add)
    with BuildSketch(Plane.XY.offset(30)):
        with Locations((0, 52.396218425)):
            Circle(SKETCH18_R)
    extrude(amount=BOSS_EXTRUDE11_DEPTH)

    # Sketch19 → Boss-Extrude12 (add)
    with BuildSketch(Plane.XY.offset(31)):
        with Locations((0, 52.396218425)):
            Circle(SKETCH19_R)
    extrude(amount=BOSS_EXTRUDE12_DEPTH)

    # Sketch20 → Boss-Extrude13 (add)
    with BuildSketch(Plane.XY.offset(46)):
        with Locations((0, 52.396218425)):
            Circle(SKETCH20_R)
    extrude(amount=BOSS_EXTRUDE13_DEPTH)

    # Sketch21 → Boss-Extrude14 (add)
    with BuildSketch(Plane.XY.offset(50)):
        with Locations((0, 52.396218425)):
            Circle(SKETCH21_R)
    extrude(amount=BOSS_EXTRUDE14_DEPTH)

    # Sketch22 → Boss-Extrude15 (add)
    with BuildSketch(Plane(origin=(0, 0, 20), x_dir=(-1, 0, 0), z_dir=(0, 0, -1))):
        with Locations(Location((0, 59.519830647, 0), (0, 0, 180))):
            Circle(SKETCH22_R)
    extrude(amount=BOSS_EXTRUDE15_DEPTH)

    # Sketch23 → Boss-Extrude16 (add)
    with BuildSketch(Plane(origin=(0, 0, 8), x_dir=(-1, 0, 0), z_dir=(0, 0, -1))):
        with Locations((0, 59.519830647)):
            Circle(SKETCH23_R)
        Polygon((2.679035332, 57.597233825), (3.004535355, 60.878644891), (0.325500023, 62.801241713), (-2.679035332, 61.442427469), (-3.004535355, 58.161016403), (-0.325500023, 56.238419581), align=None, mode=Mode.SUBTRACT)
    extrude(amount=BOSS_EXTRUDE16_DEPTH)

    # Sketch24 → Boss-Extrude17 (add)
    with BuildSketch(Plane(origin=(0, 0, -30), x_dir=(-1, 0, 0), z_dir=(0, 0, -1))):
        with Locations(Location((0, 38.12935067, 0), (0, 0, 180))):
            Circle(SKETCH24_R)
    extrude(amount=BOSS_EXTRUDE17_DEPTH)


solid = part_1.part
